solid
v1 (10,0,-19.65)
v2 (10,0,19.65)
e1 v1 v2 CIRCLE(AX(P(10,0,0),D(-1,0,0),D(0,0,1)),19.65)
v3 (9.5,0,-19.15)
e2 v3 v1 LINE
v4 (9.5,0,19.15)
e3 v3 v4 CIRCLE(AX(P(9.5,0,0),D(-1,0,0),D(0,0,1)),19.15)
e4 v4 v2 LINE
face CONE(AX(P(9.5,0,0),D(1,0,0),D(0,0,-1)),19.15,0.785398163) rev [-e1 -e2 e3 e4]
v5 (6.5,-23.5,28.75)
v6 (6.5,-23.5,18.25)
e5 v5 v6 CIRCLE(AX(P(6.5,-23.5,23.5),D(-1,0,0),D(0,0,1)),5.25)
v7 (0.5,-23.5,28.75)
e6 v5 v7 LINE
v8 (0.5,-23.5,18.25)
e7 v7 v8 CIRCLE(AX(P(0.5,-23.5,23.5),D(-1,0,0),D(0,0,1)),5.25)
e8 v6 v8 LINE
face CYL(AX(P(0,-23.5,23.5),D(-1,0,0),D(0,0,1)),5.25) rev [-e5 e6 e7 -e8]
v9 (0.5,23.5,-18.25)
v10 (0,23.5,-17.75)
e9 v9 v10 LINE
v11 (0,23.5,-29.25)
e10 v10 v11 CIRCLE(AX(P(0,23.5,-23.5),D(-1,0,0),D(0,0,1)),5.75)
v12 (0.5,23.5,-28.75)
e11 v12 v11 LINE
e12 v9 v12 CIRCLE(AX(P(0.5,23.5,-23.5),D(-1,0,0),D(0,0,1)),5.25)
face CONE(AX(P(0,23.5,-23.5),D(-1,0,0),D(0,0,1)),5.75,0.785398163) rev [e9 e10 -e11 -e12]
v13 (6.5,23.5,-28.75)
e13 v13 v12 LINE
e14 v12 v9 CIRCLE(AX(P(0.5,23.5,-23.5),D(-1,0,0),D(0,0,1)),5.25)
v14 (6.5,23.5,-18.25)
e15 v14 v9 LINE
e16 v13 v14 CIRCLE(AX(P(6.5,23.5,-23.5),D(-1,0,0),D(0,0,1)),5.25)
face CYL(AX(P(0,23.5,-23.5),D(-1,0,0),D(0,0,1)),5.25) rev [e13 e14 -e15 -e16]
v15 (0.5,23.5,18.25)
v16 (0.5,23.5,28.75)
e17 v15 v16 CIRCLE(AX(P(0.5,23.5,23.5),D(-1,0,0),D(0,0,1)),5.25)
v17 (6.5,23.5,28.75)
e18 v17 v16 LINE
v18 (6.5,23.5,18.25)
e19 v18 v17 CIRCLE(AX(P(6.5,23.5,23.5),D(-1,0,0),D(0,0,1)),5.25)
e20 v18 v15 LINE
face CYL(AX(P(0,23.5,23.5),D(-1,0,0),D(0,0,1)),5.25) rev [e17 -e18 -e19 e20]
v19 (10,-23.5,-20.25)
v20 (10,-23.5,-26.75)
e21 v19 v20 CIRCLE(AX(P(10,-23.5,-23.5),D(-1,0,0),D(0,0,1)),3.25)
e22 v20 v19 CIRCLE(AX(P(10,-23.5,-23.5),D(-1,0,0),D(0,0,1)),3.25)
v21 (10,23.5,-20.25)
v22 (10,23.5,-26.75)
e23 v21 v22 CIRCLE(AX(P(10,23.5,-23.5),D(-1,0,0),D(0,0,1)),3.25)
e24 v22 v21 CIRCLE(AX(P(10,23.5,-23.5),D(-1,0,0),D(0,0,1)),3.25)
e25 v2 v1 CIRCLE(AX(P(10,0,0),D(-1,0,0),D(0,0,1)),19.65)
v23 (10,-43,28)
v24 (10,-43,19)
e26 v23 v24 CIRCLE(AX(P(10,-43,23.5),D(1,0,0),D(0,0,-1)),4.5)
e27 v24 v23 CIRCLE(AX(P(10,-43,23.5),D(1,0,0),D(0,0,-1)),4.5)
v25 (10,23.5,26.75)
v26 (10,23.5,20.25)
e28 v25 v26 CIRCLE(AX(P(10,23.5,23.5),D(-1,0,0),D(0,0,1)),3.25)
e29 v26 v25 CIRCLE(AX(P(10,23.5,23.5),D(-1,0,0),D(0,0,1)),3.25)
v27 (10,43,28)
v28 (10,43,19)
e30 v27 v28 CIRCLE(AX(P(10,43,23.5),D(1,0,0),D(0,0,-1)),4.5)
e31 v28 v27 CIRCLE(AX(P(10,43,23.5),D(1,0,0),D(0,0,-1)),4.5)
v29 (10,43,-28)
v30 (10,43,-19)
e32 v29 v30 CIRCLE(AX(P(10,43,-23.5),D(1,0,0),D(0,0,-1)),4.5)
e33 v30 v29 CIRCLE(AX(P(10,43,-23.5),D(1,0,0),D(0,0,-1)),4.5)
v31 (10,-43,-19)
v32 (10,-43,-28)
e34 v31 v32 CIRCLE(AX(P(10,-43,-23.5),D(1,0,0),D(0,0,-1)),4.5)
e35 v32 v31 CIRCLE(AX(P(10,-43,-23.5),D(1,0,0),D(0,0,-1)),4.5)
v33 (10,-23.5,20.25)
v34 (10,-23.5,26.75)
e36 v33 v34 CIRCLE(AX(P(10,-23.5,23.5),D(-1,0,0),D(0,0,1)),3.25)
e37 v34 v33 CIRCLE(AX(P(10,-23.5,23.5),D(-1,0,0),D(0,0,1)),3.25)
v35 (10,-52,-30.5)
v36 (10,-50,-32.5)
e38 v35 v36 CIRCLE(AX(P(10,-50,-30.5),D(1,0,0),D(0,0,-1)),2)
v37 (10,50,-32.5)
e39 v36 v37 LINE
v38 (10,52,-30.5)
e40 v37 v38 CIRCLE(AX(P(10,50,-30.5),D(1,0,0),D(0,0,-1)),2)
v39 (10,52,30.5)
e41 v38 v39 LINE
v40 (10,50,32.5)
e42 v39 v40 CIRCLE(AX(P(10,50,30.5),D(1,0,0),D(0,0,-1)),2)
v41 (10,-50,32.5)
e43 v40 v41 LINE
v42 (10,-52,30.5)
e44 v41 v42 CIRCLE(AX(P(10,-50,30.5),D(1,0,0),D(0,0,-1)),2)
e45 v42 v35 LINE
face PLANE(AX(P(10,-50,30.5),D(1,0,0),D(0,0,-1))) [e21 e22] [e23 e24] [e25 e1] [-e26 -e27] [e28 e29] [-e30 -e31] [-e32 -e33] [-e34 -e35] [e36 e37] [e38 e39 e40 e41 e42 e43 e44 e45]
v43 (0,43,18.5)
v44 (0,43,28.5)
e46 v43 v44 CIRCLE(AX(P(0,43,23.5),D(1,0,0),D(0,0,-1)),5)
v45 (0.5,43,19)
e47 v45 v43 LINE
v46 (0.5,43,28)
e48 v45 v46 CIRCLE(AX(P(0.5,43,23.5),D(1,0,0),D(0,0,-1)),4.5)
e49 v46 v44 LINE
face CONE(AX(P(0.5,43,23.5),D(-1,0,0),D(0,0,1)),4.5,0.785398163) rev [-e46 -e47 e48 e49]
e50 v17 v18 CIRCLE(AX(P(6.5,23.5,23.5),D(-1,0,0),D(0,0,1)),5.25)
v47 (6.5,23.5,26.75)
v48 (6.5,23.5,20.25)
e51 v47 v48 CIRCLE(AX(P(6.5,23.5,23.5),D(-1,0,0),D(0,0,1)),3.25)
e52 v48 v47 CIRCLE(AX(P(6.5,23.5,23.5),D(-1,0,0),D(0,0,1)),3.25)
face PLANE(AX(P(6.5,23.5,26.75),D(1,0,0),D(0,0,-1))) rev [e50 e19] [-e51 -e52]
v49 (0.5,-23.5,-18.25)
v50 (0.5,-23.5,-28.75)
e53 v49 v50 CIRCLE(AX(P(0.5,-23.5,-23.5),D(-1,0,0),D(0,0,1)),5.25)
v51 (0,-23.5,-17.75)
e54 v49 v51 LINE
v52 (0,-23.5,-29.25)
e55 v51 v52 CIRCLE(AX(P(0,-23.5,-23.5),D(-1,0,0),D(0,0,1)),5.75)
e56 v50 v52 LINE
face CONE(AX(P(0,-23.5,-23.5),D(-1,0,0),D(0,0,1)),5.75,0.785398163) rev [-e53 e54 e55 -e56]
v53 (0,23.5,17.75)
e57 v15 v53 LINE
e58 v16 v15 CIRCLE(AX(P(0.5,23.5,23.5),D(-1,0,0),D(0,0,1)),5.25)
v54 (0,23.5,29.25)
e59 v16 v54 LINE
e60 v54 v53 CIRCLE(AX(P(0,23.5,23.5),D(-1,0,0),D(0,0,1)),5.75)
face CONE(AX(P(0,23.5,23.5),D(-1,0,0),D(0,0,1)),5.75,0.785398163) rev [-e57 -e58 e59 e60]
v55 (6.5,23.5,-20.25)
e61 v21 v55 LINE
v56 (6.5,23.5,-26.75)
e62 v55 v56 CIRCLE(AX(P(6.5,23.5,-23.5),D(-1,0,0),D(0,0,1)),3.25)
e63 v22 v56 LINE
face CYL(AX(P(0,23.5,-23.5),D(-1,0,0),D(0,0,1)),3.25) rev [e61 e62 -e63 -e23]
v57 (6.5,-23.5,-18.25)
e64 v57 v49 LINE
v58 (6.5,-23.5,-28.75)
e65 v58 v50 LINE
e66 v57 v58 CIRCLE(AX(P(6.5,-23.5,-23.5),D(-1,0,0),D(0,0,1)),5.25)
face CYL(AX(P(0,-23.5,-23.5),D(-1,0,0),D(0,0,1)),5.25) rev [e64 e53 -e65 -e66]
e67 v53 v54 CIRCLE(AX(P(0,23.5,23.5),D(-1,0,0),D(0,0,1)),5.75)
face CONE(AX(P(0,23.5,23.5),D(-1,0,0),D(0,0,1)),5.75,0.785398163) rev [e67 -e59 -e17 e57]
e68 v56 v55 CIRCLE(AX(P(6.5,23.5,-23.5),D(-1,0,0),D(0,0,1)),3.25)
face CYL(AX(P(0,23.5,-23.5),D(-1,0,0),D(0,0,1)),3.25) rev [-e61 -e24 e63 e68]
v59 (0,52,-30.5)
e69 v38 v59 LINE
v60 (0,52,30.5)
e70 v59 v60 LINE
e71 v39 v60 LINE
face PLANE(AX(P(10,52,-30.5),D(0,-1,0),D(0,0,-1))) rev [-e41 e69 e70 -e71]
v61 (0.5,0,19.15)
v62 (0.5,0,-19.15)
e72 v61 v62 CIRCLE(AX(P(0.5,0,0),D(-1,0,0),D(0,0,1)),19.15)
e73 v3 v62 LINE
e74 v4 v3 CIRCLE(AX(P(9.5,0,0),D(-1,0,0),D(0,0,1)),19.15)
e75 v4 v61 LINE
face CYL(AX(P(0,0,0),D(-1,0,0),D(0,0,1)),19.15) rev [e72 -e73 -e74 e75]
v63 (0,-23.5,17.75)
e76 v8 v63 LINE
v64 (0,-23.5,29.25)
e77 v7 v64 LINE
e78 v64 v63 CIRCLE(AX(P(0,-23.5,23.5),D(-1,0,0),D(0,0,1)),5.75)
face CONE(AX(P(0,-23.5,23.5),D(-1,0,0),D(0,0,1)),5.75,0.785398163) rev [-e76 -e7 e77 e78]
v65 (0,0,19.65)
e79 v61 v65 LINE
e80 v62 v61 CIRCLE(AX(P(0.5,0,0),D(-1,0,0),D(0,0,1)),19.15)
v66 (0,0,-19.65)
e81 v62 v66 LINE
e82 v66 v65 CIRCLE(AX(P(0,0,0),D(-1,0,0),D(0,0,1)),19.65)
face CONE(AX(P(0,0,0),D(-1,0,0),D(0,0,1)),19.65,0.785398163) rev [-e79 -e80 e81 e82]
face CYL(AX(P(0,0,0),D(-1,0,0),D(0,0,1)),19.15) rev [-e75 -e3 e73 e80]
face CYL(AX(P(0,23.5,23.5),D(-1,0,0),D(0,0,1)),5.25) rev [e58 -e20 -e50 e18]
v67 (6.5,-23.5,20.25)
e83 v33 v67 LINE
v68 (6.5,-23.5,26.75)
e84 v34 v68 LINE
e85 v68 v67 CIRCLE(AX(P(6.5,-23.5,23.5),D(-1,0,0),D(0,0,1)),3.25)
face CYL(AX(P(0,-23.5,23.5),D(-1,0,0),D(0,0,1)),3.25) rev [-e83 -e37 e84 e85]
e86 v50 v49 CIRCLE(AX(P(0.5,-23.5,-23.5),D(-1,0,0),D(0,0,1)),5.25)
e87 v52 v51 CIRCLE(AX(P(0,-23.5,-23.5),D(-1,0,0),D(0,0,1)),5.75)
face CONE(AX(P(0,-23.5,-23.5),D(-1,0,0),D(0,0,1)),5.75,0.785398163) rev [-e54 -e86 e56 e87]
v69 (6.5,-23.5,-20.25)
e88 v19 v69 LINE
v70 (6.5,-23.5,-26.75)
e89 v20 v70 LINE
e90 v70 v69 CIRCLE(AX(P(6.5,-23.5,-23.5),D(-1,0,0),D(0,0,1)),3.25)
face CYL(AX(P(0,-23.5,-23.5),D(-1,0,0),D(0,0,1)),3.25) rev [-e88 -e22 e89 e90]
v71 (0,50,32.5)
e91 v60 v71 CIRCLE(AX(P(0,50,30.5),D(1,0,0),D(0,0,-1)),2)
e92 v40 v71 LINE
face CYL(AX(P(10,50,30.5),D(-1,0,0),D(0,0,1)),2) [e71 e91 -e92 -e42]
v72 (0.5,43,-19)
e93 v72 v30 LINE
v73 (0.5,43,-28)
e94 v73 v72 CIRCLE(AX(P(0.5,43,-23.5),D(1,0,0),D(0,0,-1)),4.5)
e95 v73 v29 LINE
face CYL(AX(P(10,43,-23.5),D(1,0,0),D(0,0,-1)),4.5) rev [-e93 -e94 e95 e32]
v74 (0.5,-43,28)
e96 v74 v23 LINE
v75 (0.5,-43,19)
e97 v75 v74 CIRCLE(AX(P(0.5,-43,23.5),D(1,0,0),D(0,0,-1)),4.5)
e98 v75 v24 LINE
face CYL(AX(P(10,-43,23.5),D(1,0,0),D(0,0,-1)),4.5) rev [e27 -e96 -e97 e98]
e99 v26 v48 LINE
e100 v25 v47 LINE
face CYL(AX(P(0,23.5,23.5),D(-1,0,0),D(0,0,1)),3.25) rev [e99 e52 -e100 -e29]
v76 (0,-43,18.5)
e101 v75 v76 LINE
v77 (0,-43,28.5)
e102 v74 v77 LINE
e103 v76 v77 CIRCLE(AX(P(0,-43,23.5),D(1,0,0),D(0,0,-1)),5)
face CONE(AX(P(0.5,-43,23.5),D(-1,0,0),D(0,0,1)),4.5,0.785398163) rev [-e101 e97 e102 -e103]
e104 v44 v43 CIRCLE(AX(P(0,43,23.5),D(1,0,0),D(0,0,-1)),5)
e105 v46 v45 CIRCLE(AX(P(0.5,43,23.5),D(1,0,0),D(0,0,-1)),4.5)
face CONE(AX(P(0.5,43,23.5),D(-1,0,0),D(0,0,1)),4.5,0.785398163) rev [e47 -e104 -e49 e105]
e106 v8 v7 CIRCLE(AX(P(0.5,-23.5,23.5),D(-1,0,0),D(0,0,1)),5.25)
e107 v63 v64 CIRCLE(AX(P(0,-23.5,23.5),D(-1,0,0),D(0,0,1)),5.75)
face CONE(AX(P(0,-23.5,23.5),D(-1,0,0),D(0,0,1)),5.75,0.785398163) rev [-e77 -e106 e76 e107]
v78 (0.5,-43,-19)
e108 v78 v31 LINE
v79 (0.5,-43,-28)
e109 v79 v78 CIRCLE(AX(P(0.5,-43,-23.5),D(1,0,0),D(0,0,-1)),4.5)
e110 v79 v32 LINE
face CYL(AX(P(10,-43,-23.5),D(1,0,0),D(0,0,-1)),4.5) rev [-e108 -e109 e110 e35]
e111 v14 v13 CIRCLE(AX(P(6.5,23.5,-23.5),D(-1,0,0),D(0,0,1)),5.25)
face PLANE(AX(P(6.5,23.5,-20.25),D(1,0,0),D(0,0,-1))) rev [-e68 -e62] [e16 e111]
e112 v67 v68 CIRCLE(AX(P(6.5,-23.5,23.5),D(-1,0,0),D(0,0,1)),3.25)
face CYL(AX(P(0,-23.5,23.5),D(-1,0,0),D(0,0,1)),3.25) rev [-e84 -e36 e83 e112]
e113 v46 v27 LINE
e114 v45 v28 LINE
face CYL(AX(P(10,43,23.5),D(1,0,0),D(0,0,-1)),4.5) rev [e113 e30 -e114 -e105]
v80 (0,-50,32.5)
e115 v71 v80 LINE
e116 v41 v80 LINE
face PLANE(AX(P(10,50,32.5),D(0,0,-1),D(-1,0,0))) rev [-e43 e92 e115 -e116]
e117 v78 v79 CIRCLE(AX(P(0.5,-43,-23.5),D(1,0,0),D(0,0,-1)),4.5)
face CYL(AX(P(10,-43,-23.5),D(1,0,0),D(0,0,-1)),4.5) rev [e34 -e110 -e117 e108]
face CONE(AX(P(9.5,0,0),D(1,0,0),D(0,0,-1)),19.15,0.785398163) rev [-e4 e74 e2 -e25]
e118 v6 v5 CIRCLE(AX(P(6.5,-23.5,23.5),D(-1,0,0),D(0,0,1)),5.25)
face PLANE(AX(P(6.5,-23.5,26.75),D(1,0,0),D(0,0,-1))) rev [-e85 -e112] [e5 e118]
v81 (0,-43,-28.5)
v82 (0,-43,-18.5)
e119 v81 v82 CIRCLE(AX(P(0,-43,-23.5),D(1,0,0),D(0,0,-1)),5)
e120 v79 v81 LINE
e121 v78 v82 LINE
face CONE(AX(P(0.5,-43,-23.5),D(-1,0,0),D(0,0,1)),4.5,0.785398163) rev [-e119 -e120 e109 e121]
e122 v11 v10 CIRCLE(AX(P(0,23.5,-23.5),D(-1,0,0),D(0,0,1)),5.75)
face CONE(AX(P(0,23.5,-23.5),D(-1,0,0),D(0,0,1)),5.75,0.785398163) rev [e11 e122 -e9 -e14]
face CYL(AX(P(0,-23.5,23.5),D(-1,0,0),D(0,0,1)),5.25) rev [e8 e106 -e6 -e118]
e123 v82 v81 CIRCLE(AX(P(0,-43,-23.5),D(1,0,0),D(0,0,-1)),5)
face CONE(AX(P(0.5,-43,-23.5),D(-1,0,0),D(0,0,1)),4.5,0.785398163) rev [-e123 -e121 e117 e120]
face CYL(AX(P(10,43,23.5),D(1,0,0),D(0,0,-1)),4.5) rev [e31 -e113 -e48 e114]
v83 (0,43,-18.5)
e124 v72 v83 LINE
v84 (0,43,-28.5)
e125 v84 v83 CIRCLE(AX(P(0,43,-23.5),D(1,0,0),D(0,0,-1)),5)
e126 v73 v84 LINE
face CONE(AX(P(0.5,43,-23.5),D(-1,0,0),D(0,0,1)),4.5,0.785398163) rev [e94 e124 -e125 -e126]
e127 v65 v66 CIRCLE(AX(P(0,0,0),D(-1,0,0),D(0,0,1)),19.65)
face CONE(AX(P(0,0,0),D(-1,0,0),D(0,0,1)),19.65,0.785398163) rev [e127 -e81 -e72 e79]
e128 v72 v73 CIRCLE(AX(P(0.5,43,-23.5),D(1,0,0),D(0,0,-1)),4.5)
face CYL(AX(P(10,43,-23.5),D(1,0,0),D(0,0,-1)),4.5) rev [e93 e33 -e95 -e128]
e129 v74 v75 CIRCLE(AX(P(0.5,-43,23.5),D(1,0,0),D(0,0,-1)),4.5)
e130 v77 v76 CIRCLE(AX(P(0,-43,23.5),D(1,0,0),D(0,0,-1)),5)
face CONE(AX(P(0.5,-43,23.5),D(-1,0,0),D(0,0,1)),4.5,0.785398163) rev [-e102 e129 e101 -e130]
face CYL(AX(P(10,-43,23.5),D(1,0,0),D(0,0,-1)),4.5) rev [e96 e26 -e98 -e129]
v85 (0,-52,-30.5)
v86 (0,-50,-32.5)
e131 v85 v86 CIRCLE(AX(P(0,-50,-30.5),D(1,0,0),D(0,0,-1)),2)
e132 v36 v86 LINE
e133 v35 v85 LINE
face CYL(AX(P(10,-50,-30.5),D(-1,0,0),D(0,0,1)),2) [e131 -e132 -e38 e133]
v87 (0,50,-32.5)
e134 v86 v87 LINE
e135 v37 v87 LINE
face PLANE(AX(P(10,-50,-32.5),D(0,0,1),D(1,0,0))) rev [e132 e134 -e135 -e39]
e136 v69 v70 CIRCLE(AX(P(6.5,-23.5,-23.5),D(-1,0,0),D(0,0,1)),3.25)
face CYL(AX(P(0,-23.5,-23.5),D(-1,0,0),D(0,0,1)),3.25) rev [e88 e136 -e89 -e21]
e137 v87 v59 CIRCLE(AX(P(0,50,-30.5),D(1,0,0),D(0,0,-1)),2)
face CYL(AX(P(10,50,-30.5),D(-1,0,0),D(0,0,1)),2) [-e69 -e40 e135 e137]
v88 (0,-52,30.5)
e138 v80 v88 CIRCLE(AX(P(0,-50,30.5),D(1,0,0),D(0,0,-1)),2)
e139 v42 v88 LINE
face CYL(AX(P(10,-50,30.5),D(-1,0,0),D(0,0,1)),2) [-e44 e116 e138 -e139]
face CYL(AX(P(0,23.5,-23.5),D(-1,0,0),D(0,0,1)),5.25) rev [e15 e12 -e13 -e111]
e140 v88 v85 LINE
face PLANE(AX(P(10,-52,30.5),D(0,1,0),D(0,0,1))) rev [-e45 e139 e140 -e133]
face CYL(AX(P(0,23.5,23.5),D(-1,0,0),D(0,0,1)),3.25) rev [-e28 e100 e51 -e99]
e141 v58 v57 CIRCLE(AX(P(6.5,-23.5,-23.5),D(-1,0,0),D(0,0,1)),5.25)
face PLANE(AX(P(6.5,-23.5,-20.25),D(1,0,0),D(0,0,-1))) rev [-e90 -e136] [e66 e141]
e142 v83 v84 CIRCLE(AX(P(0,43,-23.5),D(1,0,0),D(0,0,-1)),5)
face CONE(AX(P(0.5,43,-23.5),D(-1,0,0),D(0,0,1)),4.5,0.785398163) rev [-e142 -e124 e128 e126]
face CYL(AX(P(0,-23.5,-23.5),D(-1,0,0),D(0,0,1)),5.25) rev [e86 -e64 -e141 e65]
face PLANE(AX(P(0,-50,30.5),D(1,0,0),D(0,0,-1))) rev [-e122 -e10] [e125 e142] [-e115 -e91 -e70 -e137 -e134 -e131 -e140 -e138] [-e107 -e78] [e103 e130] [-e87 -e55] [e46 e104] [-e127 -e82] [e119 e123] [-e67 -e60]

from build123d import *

# Parameters (mm, degrees)
BOSS_EXTRUDE1_DEPTH  = 10
LPATTERN1_COUNT      = 2
LPATTERN1_PITCH      = 47
LPATTERN1_COUNT_DIR2 = 2
LPATTERN1_PITCH_DIR2 = 47
LPATTERN2_COUNT      = 2
LPATTERN2_PITCH      = 47
LPATTERN2_COUNT_DIR2 = 2
LPATTERN2_PITCH_DIR2 = 86


with BuildPart() as part:
    # Sketch1 → Boss-Extrude1 (new body)
    with BuildSketch(Plane(origin=(0, 0, 0), x_dir=(0, 0, -1), z_dir=(1, 0, 0))):
        with BuildLine():
            Line((-30.5, -52), (30.5, -52))
            ThreePointArc((30.5, -52), (31.914213562, -51.414213562), (32.5, -50))
            Line((32.5, -50), (32.5, 50))
            ThreePointArc((32.5, 50), (31.914213562, 51.414213562), (30.5, 52))
            Line((30.5, 52), (-30.5, 52))
            ThreePointArc((-30.5, 52), (-31.914213562, 51.414213562), (-32.5, 50))
            Line((-32.5, 50), (-32.5, -50))
            ThreePointArc((-32.5, -50), (-31.914213562, -51.414213562), (-30.5, -52))
        make_face()
    extrude(amount=BOSS_EXTRUDE1_DEPTH)

    # Sketch2 → Cut-Revolve1 (revolve, cut)
    with BuildSketch(Plane(origin=(0, 0, 0), x_dir=(1, 0, 0), z_dir=(0, 1, 0))):
        Polygon((10, 0), (10, -19.65), (9.5, -19.15), (0.5, -19.15), (0, -19.65), (0, 0), align=None)
    revolve(axis=Axis((0, 0, 0), (1, 0, 0)), mode=Mode.SUBTRACT)

    # Sketch3 → Cut-Revolve2 (revolve, cut)
    with BuildSketch(Plane(origin=(0, -23.5, 0), x_dir=(1, 0, 0), z_dir=(0, 1, 0))):
        Polygon((10, 23.5), (10, 20.25), (6.5, 20.25), (6.5, 18.25), (0.5, 18.25), (0, 17.75), (0, 23.5), align=None)
    cut_revolve2 = revolve(axis=Axis((0, -23.5, -23.5), (1, 0, 0)), mode=Mode.SUBTRACT)

    # LPattern1: Cut-Revolve2 2 × 2
    with Locations(*[(0, i * LPATTERN1_PITCH, j * LPATTERN1_PITCH_DIR2) for i in range(LPATTERN1_COUNT) for j in range(LPATTERN1_COUNT_DIR2) if (i, j) != (0, 0)]):
        add(cut_revolve2, mode=Mode.SUBTRACT)

    # Sketch5 → Cut-Revolve3 (revolve, cut)
    with BuildSketch(Plane(origin=(0, -43, 0), x_dir=(1, 0, 0), z_dir=(0, 1, 0))):
        Polygon((0, -23.5), (0, -18.5), (0.5, -19), (10, -19), (10, -23.5), align=None)
    cut_revolve3 = revolve(axis=Axis((10, -43, 23.5), (-1, 0, 0)), mode=Mode.SUBTRACT)

    # LPattern2: Cut-Revolve3 2 × 2
    with Locations(*[(0, j * LPATTERN2_PITCH_DIR2, -i * LPATTERN2_PITCH) for i in range(LPATTERN2_COUNT) for j in range(LPATTERN2_COUNT_DIR2) if (i, j) != (0, 0)]):
        add(cut_revolve3, mode=Mode.SUBTRACT)


solid = part.part
